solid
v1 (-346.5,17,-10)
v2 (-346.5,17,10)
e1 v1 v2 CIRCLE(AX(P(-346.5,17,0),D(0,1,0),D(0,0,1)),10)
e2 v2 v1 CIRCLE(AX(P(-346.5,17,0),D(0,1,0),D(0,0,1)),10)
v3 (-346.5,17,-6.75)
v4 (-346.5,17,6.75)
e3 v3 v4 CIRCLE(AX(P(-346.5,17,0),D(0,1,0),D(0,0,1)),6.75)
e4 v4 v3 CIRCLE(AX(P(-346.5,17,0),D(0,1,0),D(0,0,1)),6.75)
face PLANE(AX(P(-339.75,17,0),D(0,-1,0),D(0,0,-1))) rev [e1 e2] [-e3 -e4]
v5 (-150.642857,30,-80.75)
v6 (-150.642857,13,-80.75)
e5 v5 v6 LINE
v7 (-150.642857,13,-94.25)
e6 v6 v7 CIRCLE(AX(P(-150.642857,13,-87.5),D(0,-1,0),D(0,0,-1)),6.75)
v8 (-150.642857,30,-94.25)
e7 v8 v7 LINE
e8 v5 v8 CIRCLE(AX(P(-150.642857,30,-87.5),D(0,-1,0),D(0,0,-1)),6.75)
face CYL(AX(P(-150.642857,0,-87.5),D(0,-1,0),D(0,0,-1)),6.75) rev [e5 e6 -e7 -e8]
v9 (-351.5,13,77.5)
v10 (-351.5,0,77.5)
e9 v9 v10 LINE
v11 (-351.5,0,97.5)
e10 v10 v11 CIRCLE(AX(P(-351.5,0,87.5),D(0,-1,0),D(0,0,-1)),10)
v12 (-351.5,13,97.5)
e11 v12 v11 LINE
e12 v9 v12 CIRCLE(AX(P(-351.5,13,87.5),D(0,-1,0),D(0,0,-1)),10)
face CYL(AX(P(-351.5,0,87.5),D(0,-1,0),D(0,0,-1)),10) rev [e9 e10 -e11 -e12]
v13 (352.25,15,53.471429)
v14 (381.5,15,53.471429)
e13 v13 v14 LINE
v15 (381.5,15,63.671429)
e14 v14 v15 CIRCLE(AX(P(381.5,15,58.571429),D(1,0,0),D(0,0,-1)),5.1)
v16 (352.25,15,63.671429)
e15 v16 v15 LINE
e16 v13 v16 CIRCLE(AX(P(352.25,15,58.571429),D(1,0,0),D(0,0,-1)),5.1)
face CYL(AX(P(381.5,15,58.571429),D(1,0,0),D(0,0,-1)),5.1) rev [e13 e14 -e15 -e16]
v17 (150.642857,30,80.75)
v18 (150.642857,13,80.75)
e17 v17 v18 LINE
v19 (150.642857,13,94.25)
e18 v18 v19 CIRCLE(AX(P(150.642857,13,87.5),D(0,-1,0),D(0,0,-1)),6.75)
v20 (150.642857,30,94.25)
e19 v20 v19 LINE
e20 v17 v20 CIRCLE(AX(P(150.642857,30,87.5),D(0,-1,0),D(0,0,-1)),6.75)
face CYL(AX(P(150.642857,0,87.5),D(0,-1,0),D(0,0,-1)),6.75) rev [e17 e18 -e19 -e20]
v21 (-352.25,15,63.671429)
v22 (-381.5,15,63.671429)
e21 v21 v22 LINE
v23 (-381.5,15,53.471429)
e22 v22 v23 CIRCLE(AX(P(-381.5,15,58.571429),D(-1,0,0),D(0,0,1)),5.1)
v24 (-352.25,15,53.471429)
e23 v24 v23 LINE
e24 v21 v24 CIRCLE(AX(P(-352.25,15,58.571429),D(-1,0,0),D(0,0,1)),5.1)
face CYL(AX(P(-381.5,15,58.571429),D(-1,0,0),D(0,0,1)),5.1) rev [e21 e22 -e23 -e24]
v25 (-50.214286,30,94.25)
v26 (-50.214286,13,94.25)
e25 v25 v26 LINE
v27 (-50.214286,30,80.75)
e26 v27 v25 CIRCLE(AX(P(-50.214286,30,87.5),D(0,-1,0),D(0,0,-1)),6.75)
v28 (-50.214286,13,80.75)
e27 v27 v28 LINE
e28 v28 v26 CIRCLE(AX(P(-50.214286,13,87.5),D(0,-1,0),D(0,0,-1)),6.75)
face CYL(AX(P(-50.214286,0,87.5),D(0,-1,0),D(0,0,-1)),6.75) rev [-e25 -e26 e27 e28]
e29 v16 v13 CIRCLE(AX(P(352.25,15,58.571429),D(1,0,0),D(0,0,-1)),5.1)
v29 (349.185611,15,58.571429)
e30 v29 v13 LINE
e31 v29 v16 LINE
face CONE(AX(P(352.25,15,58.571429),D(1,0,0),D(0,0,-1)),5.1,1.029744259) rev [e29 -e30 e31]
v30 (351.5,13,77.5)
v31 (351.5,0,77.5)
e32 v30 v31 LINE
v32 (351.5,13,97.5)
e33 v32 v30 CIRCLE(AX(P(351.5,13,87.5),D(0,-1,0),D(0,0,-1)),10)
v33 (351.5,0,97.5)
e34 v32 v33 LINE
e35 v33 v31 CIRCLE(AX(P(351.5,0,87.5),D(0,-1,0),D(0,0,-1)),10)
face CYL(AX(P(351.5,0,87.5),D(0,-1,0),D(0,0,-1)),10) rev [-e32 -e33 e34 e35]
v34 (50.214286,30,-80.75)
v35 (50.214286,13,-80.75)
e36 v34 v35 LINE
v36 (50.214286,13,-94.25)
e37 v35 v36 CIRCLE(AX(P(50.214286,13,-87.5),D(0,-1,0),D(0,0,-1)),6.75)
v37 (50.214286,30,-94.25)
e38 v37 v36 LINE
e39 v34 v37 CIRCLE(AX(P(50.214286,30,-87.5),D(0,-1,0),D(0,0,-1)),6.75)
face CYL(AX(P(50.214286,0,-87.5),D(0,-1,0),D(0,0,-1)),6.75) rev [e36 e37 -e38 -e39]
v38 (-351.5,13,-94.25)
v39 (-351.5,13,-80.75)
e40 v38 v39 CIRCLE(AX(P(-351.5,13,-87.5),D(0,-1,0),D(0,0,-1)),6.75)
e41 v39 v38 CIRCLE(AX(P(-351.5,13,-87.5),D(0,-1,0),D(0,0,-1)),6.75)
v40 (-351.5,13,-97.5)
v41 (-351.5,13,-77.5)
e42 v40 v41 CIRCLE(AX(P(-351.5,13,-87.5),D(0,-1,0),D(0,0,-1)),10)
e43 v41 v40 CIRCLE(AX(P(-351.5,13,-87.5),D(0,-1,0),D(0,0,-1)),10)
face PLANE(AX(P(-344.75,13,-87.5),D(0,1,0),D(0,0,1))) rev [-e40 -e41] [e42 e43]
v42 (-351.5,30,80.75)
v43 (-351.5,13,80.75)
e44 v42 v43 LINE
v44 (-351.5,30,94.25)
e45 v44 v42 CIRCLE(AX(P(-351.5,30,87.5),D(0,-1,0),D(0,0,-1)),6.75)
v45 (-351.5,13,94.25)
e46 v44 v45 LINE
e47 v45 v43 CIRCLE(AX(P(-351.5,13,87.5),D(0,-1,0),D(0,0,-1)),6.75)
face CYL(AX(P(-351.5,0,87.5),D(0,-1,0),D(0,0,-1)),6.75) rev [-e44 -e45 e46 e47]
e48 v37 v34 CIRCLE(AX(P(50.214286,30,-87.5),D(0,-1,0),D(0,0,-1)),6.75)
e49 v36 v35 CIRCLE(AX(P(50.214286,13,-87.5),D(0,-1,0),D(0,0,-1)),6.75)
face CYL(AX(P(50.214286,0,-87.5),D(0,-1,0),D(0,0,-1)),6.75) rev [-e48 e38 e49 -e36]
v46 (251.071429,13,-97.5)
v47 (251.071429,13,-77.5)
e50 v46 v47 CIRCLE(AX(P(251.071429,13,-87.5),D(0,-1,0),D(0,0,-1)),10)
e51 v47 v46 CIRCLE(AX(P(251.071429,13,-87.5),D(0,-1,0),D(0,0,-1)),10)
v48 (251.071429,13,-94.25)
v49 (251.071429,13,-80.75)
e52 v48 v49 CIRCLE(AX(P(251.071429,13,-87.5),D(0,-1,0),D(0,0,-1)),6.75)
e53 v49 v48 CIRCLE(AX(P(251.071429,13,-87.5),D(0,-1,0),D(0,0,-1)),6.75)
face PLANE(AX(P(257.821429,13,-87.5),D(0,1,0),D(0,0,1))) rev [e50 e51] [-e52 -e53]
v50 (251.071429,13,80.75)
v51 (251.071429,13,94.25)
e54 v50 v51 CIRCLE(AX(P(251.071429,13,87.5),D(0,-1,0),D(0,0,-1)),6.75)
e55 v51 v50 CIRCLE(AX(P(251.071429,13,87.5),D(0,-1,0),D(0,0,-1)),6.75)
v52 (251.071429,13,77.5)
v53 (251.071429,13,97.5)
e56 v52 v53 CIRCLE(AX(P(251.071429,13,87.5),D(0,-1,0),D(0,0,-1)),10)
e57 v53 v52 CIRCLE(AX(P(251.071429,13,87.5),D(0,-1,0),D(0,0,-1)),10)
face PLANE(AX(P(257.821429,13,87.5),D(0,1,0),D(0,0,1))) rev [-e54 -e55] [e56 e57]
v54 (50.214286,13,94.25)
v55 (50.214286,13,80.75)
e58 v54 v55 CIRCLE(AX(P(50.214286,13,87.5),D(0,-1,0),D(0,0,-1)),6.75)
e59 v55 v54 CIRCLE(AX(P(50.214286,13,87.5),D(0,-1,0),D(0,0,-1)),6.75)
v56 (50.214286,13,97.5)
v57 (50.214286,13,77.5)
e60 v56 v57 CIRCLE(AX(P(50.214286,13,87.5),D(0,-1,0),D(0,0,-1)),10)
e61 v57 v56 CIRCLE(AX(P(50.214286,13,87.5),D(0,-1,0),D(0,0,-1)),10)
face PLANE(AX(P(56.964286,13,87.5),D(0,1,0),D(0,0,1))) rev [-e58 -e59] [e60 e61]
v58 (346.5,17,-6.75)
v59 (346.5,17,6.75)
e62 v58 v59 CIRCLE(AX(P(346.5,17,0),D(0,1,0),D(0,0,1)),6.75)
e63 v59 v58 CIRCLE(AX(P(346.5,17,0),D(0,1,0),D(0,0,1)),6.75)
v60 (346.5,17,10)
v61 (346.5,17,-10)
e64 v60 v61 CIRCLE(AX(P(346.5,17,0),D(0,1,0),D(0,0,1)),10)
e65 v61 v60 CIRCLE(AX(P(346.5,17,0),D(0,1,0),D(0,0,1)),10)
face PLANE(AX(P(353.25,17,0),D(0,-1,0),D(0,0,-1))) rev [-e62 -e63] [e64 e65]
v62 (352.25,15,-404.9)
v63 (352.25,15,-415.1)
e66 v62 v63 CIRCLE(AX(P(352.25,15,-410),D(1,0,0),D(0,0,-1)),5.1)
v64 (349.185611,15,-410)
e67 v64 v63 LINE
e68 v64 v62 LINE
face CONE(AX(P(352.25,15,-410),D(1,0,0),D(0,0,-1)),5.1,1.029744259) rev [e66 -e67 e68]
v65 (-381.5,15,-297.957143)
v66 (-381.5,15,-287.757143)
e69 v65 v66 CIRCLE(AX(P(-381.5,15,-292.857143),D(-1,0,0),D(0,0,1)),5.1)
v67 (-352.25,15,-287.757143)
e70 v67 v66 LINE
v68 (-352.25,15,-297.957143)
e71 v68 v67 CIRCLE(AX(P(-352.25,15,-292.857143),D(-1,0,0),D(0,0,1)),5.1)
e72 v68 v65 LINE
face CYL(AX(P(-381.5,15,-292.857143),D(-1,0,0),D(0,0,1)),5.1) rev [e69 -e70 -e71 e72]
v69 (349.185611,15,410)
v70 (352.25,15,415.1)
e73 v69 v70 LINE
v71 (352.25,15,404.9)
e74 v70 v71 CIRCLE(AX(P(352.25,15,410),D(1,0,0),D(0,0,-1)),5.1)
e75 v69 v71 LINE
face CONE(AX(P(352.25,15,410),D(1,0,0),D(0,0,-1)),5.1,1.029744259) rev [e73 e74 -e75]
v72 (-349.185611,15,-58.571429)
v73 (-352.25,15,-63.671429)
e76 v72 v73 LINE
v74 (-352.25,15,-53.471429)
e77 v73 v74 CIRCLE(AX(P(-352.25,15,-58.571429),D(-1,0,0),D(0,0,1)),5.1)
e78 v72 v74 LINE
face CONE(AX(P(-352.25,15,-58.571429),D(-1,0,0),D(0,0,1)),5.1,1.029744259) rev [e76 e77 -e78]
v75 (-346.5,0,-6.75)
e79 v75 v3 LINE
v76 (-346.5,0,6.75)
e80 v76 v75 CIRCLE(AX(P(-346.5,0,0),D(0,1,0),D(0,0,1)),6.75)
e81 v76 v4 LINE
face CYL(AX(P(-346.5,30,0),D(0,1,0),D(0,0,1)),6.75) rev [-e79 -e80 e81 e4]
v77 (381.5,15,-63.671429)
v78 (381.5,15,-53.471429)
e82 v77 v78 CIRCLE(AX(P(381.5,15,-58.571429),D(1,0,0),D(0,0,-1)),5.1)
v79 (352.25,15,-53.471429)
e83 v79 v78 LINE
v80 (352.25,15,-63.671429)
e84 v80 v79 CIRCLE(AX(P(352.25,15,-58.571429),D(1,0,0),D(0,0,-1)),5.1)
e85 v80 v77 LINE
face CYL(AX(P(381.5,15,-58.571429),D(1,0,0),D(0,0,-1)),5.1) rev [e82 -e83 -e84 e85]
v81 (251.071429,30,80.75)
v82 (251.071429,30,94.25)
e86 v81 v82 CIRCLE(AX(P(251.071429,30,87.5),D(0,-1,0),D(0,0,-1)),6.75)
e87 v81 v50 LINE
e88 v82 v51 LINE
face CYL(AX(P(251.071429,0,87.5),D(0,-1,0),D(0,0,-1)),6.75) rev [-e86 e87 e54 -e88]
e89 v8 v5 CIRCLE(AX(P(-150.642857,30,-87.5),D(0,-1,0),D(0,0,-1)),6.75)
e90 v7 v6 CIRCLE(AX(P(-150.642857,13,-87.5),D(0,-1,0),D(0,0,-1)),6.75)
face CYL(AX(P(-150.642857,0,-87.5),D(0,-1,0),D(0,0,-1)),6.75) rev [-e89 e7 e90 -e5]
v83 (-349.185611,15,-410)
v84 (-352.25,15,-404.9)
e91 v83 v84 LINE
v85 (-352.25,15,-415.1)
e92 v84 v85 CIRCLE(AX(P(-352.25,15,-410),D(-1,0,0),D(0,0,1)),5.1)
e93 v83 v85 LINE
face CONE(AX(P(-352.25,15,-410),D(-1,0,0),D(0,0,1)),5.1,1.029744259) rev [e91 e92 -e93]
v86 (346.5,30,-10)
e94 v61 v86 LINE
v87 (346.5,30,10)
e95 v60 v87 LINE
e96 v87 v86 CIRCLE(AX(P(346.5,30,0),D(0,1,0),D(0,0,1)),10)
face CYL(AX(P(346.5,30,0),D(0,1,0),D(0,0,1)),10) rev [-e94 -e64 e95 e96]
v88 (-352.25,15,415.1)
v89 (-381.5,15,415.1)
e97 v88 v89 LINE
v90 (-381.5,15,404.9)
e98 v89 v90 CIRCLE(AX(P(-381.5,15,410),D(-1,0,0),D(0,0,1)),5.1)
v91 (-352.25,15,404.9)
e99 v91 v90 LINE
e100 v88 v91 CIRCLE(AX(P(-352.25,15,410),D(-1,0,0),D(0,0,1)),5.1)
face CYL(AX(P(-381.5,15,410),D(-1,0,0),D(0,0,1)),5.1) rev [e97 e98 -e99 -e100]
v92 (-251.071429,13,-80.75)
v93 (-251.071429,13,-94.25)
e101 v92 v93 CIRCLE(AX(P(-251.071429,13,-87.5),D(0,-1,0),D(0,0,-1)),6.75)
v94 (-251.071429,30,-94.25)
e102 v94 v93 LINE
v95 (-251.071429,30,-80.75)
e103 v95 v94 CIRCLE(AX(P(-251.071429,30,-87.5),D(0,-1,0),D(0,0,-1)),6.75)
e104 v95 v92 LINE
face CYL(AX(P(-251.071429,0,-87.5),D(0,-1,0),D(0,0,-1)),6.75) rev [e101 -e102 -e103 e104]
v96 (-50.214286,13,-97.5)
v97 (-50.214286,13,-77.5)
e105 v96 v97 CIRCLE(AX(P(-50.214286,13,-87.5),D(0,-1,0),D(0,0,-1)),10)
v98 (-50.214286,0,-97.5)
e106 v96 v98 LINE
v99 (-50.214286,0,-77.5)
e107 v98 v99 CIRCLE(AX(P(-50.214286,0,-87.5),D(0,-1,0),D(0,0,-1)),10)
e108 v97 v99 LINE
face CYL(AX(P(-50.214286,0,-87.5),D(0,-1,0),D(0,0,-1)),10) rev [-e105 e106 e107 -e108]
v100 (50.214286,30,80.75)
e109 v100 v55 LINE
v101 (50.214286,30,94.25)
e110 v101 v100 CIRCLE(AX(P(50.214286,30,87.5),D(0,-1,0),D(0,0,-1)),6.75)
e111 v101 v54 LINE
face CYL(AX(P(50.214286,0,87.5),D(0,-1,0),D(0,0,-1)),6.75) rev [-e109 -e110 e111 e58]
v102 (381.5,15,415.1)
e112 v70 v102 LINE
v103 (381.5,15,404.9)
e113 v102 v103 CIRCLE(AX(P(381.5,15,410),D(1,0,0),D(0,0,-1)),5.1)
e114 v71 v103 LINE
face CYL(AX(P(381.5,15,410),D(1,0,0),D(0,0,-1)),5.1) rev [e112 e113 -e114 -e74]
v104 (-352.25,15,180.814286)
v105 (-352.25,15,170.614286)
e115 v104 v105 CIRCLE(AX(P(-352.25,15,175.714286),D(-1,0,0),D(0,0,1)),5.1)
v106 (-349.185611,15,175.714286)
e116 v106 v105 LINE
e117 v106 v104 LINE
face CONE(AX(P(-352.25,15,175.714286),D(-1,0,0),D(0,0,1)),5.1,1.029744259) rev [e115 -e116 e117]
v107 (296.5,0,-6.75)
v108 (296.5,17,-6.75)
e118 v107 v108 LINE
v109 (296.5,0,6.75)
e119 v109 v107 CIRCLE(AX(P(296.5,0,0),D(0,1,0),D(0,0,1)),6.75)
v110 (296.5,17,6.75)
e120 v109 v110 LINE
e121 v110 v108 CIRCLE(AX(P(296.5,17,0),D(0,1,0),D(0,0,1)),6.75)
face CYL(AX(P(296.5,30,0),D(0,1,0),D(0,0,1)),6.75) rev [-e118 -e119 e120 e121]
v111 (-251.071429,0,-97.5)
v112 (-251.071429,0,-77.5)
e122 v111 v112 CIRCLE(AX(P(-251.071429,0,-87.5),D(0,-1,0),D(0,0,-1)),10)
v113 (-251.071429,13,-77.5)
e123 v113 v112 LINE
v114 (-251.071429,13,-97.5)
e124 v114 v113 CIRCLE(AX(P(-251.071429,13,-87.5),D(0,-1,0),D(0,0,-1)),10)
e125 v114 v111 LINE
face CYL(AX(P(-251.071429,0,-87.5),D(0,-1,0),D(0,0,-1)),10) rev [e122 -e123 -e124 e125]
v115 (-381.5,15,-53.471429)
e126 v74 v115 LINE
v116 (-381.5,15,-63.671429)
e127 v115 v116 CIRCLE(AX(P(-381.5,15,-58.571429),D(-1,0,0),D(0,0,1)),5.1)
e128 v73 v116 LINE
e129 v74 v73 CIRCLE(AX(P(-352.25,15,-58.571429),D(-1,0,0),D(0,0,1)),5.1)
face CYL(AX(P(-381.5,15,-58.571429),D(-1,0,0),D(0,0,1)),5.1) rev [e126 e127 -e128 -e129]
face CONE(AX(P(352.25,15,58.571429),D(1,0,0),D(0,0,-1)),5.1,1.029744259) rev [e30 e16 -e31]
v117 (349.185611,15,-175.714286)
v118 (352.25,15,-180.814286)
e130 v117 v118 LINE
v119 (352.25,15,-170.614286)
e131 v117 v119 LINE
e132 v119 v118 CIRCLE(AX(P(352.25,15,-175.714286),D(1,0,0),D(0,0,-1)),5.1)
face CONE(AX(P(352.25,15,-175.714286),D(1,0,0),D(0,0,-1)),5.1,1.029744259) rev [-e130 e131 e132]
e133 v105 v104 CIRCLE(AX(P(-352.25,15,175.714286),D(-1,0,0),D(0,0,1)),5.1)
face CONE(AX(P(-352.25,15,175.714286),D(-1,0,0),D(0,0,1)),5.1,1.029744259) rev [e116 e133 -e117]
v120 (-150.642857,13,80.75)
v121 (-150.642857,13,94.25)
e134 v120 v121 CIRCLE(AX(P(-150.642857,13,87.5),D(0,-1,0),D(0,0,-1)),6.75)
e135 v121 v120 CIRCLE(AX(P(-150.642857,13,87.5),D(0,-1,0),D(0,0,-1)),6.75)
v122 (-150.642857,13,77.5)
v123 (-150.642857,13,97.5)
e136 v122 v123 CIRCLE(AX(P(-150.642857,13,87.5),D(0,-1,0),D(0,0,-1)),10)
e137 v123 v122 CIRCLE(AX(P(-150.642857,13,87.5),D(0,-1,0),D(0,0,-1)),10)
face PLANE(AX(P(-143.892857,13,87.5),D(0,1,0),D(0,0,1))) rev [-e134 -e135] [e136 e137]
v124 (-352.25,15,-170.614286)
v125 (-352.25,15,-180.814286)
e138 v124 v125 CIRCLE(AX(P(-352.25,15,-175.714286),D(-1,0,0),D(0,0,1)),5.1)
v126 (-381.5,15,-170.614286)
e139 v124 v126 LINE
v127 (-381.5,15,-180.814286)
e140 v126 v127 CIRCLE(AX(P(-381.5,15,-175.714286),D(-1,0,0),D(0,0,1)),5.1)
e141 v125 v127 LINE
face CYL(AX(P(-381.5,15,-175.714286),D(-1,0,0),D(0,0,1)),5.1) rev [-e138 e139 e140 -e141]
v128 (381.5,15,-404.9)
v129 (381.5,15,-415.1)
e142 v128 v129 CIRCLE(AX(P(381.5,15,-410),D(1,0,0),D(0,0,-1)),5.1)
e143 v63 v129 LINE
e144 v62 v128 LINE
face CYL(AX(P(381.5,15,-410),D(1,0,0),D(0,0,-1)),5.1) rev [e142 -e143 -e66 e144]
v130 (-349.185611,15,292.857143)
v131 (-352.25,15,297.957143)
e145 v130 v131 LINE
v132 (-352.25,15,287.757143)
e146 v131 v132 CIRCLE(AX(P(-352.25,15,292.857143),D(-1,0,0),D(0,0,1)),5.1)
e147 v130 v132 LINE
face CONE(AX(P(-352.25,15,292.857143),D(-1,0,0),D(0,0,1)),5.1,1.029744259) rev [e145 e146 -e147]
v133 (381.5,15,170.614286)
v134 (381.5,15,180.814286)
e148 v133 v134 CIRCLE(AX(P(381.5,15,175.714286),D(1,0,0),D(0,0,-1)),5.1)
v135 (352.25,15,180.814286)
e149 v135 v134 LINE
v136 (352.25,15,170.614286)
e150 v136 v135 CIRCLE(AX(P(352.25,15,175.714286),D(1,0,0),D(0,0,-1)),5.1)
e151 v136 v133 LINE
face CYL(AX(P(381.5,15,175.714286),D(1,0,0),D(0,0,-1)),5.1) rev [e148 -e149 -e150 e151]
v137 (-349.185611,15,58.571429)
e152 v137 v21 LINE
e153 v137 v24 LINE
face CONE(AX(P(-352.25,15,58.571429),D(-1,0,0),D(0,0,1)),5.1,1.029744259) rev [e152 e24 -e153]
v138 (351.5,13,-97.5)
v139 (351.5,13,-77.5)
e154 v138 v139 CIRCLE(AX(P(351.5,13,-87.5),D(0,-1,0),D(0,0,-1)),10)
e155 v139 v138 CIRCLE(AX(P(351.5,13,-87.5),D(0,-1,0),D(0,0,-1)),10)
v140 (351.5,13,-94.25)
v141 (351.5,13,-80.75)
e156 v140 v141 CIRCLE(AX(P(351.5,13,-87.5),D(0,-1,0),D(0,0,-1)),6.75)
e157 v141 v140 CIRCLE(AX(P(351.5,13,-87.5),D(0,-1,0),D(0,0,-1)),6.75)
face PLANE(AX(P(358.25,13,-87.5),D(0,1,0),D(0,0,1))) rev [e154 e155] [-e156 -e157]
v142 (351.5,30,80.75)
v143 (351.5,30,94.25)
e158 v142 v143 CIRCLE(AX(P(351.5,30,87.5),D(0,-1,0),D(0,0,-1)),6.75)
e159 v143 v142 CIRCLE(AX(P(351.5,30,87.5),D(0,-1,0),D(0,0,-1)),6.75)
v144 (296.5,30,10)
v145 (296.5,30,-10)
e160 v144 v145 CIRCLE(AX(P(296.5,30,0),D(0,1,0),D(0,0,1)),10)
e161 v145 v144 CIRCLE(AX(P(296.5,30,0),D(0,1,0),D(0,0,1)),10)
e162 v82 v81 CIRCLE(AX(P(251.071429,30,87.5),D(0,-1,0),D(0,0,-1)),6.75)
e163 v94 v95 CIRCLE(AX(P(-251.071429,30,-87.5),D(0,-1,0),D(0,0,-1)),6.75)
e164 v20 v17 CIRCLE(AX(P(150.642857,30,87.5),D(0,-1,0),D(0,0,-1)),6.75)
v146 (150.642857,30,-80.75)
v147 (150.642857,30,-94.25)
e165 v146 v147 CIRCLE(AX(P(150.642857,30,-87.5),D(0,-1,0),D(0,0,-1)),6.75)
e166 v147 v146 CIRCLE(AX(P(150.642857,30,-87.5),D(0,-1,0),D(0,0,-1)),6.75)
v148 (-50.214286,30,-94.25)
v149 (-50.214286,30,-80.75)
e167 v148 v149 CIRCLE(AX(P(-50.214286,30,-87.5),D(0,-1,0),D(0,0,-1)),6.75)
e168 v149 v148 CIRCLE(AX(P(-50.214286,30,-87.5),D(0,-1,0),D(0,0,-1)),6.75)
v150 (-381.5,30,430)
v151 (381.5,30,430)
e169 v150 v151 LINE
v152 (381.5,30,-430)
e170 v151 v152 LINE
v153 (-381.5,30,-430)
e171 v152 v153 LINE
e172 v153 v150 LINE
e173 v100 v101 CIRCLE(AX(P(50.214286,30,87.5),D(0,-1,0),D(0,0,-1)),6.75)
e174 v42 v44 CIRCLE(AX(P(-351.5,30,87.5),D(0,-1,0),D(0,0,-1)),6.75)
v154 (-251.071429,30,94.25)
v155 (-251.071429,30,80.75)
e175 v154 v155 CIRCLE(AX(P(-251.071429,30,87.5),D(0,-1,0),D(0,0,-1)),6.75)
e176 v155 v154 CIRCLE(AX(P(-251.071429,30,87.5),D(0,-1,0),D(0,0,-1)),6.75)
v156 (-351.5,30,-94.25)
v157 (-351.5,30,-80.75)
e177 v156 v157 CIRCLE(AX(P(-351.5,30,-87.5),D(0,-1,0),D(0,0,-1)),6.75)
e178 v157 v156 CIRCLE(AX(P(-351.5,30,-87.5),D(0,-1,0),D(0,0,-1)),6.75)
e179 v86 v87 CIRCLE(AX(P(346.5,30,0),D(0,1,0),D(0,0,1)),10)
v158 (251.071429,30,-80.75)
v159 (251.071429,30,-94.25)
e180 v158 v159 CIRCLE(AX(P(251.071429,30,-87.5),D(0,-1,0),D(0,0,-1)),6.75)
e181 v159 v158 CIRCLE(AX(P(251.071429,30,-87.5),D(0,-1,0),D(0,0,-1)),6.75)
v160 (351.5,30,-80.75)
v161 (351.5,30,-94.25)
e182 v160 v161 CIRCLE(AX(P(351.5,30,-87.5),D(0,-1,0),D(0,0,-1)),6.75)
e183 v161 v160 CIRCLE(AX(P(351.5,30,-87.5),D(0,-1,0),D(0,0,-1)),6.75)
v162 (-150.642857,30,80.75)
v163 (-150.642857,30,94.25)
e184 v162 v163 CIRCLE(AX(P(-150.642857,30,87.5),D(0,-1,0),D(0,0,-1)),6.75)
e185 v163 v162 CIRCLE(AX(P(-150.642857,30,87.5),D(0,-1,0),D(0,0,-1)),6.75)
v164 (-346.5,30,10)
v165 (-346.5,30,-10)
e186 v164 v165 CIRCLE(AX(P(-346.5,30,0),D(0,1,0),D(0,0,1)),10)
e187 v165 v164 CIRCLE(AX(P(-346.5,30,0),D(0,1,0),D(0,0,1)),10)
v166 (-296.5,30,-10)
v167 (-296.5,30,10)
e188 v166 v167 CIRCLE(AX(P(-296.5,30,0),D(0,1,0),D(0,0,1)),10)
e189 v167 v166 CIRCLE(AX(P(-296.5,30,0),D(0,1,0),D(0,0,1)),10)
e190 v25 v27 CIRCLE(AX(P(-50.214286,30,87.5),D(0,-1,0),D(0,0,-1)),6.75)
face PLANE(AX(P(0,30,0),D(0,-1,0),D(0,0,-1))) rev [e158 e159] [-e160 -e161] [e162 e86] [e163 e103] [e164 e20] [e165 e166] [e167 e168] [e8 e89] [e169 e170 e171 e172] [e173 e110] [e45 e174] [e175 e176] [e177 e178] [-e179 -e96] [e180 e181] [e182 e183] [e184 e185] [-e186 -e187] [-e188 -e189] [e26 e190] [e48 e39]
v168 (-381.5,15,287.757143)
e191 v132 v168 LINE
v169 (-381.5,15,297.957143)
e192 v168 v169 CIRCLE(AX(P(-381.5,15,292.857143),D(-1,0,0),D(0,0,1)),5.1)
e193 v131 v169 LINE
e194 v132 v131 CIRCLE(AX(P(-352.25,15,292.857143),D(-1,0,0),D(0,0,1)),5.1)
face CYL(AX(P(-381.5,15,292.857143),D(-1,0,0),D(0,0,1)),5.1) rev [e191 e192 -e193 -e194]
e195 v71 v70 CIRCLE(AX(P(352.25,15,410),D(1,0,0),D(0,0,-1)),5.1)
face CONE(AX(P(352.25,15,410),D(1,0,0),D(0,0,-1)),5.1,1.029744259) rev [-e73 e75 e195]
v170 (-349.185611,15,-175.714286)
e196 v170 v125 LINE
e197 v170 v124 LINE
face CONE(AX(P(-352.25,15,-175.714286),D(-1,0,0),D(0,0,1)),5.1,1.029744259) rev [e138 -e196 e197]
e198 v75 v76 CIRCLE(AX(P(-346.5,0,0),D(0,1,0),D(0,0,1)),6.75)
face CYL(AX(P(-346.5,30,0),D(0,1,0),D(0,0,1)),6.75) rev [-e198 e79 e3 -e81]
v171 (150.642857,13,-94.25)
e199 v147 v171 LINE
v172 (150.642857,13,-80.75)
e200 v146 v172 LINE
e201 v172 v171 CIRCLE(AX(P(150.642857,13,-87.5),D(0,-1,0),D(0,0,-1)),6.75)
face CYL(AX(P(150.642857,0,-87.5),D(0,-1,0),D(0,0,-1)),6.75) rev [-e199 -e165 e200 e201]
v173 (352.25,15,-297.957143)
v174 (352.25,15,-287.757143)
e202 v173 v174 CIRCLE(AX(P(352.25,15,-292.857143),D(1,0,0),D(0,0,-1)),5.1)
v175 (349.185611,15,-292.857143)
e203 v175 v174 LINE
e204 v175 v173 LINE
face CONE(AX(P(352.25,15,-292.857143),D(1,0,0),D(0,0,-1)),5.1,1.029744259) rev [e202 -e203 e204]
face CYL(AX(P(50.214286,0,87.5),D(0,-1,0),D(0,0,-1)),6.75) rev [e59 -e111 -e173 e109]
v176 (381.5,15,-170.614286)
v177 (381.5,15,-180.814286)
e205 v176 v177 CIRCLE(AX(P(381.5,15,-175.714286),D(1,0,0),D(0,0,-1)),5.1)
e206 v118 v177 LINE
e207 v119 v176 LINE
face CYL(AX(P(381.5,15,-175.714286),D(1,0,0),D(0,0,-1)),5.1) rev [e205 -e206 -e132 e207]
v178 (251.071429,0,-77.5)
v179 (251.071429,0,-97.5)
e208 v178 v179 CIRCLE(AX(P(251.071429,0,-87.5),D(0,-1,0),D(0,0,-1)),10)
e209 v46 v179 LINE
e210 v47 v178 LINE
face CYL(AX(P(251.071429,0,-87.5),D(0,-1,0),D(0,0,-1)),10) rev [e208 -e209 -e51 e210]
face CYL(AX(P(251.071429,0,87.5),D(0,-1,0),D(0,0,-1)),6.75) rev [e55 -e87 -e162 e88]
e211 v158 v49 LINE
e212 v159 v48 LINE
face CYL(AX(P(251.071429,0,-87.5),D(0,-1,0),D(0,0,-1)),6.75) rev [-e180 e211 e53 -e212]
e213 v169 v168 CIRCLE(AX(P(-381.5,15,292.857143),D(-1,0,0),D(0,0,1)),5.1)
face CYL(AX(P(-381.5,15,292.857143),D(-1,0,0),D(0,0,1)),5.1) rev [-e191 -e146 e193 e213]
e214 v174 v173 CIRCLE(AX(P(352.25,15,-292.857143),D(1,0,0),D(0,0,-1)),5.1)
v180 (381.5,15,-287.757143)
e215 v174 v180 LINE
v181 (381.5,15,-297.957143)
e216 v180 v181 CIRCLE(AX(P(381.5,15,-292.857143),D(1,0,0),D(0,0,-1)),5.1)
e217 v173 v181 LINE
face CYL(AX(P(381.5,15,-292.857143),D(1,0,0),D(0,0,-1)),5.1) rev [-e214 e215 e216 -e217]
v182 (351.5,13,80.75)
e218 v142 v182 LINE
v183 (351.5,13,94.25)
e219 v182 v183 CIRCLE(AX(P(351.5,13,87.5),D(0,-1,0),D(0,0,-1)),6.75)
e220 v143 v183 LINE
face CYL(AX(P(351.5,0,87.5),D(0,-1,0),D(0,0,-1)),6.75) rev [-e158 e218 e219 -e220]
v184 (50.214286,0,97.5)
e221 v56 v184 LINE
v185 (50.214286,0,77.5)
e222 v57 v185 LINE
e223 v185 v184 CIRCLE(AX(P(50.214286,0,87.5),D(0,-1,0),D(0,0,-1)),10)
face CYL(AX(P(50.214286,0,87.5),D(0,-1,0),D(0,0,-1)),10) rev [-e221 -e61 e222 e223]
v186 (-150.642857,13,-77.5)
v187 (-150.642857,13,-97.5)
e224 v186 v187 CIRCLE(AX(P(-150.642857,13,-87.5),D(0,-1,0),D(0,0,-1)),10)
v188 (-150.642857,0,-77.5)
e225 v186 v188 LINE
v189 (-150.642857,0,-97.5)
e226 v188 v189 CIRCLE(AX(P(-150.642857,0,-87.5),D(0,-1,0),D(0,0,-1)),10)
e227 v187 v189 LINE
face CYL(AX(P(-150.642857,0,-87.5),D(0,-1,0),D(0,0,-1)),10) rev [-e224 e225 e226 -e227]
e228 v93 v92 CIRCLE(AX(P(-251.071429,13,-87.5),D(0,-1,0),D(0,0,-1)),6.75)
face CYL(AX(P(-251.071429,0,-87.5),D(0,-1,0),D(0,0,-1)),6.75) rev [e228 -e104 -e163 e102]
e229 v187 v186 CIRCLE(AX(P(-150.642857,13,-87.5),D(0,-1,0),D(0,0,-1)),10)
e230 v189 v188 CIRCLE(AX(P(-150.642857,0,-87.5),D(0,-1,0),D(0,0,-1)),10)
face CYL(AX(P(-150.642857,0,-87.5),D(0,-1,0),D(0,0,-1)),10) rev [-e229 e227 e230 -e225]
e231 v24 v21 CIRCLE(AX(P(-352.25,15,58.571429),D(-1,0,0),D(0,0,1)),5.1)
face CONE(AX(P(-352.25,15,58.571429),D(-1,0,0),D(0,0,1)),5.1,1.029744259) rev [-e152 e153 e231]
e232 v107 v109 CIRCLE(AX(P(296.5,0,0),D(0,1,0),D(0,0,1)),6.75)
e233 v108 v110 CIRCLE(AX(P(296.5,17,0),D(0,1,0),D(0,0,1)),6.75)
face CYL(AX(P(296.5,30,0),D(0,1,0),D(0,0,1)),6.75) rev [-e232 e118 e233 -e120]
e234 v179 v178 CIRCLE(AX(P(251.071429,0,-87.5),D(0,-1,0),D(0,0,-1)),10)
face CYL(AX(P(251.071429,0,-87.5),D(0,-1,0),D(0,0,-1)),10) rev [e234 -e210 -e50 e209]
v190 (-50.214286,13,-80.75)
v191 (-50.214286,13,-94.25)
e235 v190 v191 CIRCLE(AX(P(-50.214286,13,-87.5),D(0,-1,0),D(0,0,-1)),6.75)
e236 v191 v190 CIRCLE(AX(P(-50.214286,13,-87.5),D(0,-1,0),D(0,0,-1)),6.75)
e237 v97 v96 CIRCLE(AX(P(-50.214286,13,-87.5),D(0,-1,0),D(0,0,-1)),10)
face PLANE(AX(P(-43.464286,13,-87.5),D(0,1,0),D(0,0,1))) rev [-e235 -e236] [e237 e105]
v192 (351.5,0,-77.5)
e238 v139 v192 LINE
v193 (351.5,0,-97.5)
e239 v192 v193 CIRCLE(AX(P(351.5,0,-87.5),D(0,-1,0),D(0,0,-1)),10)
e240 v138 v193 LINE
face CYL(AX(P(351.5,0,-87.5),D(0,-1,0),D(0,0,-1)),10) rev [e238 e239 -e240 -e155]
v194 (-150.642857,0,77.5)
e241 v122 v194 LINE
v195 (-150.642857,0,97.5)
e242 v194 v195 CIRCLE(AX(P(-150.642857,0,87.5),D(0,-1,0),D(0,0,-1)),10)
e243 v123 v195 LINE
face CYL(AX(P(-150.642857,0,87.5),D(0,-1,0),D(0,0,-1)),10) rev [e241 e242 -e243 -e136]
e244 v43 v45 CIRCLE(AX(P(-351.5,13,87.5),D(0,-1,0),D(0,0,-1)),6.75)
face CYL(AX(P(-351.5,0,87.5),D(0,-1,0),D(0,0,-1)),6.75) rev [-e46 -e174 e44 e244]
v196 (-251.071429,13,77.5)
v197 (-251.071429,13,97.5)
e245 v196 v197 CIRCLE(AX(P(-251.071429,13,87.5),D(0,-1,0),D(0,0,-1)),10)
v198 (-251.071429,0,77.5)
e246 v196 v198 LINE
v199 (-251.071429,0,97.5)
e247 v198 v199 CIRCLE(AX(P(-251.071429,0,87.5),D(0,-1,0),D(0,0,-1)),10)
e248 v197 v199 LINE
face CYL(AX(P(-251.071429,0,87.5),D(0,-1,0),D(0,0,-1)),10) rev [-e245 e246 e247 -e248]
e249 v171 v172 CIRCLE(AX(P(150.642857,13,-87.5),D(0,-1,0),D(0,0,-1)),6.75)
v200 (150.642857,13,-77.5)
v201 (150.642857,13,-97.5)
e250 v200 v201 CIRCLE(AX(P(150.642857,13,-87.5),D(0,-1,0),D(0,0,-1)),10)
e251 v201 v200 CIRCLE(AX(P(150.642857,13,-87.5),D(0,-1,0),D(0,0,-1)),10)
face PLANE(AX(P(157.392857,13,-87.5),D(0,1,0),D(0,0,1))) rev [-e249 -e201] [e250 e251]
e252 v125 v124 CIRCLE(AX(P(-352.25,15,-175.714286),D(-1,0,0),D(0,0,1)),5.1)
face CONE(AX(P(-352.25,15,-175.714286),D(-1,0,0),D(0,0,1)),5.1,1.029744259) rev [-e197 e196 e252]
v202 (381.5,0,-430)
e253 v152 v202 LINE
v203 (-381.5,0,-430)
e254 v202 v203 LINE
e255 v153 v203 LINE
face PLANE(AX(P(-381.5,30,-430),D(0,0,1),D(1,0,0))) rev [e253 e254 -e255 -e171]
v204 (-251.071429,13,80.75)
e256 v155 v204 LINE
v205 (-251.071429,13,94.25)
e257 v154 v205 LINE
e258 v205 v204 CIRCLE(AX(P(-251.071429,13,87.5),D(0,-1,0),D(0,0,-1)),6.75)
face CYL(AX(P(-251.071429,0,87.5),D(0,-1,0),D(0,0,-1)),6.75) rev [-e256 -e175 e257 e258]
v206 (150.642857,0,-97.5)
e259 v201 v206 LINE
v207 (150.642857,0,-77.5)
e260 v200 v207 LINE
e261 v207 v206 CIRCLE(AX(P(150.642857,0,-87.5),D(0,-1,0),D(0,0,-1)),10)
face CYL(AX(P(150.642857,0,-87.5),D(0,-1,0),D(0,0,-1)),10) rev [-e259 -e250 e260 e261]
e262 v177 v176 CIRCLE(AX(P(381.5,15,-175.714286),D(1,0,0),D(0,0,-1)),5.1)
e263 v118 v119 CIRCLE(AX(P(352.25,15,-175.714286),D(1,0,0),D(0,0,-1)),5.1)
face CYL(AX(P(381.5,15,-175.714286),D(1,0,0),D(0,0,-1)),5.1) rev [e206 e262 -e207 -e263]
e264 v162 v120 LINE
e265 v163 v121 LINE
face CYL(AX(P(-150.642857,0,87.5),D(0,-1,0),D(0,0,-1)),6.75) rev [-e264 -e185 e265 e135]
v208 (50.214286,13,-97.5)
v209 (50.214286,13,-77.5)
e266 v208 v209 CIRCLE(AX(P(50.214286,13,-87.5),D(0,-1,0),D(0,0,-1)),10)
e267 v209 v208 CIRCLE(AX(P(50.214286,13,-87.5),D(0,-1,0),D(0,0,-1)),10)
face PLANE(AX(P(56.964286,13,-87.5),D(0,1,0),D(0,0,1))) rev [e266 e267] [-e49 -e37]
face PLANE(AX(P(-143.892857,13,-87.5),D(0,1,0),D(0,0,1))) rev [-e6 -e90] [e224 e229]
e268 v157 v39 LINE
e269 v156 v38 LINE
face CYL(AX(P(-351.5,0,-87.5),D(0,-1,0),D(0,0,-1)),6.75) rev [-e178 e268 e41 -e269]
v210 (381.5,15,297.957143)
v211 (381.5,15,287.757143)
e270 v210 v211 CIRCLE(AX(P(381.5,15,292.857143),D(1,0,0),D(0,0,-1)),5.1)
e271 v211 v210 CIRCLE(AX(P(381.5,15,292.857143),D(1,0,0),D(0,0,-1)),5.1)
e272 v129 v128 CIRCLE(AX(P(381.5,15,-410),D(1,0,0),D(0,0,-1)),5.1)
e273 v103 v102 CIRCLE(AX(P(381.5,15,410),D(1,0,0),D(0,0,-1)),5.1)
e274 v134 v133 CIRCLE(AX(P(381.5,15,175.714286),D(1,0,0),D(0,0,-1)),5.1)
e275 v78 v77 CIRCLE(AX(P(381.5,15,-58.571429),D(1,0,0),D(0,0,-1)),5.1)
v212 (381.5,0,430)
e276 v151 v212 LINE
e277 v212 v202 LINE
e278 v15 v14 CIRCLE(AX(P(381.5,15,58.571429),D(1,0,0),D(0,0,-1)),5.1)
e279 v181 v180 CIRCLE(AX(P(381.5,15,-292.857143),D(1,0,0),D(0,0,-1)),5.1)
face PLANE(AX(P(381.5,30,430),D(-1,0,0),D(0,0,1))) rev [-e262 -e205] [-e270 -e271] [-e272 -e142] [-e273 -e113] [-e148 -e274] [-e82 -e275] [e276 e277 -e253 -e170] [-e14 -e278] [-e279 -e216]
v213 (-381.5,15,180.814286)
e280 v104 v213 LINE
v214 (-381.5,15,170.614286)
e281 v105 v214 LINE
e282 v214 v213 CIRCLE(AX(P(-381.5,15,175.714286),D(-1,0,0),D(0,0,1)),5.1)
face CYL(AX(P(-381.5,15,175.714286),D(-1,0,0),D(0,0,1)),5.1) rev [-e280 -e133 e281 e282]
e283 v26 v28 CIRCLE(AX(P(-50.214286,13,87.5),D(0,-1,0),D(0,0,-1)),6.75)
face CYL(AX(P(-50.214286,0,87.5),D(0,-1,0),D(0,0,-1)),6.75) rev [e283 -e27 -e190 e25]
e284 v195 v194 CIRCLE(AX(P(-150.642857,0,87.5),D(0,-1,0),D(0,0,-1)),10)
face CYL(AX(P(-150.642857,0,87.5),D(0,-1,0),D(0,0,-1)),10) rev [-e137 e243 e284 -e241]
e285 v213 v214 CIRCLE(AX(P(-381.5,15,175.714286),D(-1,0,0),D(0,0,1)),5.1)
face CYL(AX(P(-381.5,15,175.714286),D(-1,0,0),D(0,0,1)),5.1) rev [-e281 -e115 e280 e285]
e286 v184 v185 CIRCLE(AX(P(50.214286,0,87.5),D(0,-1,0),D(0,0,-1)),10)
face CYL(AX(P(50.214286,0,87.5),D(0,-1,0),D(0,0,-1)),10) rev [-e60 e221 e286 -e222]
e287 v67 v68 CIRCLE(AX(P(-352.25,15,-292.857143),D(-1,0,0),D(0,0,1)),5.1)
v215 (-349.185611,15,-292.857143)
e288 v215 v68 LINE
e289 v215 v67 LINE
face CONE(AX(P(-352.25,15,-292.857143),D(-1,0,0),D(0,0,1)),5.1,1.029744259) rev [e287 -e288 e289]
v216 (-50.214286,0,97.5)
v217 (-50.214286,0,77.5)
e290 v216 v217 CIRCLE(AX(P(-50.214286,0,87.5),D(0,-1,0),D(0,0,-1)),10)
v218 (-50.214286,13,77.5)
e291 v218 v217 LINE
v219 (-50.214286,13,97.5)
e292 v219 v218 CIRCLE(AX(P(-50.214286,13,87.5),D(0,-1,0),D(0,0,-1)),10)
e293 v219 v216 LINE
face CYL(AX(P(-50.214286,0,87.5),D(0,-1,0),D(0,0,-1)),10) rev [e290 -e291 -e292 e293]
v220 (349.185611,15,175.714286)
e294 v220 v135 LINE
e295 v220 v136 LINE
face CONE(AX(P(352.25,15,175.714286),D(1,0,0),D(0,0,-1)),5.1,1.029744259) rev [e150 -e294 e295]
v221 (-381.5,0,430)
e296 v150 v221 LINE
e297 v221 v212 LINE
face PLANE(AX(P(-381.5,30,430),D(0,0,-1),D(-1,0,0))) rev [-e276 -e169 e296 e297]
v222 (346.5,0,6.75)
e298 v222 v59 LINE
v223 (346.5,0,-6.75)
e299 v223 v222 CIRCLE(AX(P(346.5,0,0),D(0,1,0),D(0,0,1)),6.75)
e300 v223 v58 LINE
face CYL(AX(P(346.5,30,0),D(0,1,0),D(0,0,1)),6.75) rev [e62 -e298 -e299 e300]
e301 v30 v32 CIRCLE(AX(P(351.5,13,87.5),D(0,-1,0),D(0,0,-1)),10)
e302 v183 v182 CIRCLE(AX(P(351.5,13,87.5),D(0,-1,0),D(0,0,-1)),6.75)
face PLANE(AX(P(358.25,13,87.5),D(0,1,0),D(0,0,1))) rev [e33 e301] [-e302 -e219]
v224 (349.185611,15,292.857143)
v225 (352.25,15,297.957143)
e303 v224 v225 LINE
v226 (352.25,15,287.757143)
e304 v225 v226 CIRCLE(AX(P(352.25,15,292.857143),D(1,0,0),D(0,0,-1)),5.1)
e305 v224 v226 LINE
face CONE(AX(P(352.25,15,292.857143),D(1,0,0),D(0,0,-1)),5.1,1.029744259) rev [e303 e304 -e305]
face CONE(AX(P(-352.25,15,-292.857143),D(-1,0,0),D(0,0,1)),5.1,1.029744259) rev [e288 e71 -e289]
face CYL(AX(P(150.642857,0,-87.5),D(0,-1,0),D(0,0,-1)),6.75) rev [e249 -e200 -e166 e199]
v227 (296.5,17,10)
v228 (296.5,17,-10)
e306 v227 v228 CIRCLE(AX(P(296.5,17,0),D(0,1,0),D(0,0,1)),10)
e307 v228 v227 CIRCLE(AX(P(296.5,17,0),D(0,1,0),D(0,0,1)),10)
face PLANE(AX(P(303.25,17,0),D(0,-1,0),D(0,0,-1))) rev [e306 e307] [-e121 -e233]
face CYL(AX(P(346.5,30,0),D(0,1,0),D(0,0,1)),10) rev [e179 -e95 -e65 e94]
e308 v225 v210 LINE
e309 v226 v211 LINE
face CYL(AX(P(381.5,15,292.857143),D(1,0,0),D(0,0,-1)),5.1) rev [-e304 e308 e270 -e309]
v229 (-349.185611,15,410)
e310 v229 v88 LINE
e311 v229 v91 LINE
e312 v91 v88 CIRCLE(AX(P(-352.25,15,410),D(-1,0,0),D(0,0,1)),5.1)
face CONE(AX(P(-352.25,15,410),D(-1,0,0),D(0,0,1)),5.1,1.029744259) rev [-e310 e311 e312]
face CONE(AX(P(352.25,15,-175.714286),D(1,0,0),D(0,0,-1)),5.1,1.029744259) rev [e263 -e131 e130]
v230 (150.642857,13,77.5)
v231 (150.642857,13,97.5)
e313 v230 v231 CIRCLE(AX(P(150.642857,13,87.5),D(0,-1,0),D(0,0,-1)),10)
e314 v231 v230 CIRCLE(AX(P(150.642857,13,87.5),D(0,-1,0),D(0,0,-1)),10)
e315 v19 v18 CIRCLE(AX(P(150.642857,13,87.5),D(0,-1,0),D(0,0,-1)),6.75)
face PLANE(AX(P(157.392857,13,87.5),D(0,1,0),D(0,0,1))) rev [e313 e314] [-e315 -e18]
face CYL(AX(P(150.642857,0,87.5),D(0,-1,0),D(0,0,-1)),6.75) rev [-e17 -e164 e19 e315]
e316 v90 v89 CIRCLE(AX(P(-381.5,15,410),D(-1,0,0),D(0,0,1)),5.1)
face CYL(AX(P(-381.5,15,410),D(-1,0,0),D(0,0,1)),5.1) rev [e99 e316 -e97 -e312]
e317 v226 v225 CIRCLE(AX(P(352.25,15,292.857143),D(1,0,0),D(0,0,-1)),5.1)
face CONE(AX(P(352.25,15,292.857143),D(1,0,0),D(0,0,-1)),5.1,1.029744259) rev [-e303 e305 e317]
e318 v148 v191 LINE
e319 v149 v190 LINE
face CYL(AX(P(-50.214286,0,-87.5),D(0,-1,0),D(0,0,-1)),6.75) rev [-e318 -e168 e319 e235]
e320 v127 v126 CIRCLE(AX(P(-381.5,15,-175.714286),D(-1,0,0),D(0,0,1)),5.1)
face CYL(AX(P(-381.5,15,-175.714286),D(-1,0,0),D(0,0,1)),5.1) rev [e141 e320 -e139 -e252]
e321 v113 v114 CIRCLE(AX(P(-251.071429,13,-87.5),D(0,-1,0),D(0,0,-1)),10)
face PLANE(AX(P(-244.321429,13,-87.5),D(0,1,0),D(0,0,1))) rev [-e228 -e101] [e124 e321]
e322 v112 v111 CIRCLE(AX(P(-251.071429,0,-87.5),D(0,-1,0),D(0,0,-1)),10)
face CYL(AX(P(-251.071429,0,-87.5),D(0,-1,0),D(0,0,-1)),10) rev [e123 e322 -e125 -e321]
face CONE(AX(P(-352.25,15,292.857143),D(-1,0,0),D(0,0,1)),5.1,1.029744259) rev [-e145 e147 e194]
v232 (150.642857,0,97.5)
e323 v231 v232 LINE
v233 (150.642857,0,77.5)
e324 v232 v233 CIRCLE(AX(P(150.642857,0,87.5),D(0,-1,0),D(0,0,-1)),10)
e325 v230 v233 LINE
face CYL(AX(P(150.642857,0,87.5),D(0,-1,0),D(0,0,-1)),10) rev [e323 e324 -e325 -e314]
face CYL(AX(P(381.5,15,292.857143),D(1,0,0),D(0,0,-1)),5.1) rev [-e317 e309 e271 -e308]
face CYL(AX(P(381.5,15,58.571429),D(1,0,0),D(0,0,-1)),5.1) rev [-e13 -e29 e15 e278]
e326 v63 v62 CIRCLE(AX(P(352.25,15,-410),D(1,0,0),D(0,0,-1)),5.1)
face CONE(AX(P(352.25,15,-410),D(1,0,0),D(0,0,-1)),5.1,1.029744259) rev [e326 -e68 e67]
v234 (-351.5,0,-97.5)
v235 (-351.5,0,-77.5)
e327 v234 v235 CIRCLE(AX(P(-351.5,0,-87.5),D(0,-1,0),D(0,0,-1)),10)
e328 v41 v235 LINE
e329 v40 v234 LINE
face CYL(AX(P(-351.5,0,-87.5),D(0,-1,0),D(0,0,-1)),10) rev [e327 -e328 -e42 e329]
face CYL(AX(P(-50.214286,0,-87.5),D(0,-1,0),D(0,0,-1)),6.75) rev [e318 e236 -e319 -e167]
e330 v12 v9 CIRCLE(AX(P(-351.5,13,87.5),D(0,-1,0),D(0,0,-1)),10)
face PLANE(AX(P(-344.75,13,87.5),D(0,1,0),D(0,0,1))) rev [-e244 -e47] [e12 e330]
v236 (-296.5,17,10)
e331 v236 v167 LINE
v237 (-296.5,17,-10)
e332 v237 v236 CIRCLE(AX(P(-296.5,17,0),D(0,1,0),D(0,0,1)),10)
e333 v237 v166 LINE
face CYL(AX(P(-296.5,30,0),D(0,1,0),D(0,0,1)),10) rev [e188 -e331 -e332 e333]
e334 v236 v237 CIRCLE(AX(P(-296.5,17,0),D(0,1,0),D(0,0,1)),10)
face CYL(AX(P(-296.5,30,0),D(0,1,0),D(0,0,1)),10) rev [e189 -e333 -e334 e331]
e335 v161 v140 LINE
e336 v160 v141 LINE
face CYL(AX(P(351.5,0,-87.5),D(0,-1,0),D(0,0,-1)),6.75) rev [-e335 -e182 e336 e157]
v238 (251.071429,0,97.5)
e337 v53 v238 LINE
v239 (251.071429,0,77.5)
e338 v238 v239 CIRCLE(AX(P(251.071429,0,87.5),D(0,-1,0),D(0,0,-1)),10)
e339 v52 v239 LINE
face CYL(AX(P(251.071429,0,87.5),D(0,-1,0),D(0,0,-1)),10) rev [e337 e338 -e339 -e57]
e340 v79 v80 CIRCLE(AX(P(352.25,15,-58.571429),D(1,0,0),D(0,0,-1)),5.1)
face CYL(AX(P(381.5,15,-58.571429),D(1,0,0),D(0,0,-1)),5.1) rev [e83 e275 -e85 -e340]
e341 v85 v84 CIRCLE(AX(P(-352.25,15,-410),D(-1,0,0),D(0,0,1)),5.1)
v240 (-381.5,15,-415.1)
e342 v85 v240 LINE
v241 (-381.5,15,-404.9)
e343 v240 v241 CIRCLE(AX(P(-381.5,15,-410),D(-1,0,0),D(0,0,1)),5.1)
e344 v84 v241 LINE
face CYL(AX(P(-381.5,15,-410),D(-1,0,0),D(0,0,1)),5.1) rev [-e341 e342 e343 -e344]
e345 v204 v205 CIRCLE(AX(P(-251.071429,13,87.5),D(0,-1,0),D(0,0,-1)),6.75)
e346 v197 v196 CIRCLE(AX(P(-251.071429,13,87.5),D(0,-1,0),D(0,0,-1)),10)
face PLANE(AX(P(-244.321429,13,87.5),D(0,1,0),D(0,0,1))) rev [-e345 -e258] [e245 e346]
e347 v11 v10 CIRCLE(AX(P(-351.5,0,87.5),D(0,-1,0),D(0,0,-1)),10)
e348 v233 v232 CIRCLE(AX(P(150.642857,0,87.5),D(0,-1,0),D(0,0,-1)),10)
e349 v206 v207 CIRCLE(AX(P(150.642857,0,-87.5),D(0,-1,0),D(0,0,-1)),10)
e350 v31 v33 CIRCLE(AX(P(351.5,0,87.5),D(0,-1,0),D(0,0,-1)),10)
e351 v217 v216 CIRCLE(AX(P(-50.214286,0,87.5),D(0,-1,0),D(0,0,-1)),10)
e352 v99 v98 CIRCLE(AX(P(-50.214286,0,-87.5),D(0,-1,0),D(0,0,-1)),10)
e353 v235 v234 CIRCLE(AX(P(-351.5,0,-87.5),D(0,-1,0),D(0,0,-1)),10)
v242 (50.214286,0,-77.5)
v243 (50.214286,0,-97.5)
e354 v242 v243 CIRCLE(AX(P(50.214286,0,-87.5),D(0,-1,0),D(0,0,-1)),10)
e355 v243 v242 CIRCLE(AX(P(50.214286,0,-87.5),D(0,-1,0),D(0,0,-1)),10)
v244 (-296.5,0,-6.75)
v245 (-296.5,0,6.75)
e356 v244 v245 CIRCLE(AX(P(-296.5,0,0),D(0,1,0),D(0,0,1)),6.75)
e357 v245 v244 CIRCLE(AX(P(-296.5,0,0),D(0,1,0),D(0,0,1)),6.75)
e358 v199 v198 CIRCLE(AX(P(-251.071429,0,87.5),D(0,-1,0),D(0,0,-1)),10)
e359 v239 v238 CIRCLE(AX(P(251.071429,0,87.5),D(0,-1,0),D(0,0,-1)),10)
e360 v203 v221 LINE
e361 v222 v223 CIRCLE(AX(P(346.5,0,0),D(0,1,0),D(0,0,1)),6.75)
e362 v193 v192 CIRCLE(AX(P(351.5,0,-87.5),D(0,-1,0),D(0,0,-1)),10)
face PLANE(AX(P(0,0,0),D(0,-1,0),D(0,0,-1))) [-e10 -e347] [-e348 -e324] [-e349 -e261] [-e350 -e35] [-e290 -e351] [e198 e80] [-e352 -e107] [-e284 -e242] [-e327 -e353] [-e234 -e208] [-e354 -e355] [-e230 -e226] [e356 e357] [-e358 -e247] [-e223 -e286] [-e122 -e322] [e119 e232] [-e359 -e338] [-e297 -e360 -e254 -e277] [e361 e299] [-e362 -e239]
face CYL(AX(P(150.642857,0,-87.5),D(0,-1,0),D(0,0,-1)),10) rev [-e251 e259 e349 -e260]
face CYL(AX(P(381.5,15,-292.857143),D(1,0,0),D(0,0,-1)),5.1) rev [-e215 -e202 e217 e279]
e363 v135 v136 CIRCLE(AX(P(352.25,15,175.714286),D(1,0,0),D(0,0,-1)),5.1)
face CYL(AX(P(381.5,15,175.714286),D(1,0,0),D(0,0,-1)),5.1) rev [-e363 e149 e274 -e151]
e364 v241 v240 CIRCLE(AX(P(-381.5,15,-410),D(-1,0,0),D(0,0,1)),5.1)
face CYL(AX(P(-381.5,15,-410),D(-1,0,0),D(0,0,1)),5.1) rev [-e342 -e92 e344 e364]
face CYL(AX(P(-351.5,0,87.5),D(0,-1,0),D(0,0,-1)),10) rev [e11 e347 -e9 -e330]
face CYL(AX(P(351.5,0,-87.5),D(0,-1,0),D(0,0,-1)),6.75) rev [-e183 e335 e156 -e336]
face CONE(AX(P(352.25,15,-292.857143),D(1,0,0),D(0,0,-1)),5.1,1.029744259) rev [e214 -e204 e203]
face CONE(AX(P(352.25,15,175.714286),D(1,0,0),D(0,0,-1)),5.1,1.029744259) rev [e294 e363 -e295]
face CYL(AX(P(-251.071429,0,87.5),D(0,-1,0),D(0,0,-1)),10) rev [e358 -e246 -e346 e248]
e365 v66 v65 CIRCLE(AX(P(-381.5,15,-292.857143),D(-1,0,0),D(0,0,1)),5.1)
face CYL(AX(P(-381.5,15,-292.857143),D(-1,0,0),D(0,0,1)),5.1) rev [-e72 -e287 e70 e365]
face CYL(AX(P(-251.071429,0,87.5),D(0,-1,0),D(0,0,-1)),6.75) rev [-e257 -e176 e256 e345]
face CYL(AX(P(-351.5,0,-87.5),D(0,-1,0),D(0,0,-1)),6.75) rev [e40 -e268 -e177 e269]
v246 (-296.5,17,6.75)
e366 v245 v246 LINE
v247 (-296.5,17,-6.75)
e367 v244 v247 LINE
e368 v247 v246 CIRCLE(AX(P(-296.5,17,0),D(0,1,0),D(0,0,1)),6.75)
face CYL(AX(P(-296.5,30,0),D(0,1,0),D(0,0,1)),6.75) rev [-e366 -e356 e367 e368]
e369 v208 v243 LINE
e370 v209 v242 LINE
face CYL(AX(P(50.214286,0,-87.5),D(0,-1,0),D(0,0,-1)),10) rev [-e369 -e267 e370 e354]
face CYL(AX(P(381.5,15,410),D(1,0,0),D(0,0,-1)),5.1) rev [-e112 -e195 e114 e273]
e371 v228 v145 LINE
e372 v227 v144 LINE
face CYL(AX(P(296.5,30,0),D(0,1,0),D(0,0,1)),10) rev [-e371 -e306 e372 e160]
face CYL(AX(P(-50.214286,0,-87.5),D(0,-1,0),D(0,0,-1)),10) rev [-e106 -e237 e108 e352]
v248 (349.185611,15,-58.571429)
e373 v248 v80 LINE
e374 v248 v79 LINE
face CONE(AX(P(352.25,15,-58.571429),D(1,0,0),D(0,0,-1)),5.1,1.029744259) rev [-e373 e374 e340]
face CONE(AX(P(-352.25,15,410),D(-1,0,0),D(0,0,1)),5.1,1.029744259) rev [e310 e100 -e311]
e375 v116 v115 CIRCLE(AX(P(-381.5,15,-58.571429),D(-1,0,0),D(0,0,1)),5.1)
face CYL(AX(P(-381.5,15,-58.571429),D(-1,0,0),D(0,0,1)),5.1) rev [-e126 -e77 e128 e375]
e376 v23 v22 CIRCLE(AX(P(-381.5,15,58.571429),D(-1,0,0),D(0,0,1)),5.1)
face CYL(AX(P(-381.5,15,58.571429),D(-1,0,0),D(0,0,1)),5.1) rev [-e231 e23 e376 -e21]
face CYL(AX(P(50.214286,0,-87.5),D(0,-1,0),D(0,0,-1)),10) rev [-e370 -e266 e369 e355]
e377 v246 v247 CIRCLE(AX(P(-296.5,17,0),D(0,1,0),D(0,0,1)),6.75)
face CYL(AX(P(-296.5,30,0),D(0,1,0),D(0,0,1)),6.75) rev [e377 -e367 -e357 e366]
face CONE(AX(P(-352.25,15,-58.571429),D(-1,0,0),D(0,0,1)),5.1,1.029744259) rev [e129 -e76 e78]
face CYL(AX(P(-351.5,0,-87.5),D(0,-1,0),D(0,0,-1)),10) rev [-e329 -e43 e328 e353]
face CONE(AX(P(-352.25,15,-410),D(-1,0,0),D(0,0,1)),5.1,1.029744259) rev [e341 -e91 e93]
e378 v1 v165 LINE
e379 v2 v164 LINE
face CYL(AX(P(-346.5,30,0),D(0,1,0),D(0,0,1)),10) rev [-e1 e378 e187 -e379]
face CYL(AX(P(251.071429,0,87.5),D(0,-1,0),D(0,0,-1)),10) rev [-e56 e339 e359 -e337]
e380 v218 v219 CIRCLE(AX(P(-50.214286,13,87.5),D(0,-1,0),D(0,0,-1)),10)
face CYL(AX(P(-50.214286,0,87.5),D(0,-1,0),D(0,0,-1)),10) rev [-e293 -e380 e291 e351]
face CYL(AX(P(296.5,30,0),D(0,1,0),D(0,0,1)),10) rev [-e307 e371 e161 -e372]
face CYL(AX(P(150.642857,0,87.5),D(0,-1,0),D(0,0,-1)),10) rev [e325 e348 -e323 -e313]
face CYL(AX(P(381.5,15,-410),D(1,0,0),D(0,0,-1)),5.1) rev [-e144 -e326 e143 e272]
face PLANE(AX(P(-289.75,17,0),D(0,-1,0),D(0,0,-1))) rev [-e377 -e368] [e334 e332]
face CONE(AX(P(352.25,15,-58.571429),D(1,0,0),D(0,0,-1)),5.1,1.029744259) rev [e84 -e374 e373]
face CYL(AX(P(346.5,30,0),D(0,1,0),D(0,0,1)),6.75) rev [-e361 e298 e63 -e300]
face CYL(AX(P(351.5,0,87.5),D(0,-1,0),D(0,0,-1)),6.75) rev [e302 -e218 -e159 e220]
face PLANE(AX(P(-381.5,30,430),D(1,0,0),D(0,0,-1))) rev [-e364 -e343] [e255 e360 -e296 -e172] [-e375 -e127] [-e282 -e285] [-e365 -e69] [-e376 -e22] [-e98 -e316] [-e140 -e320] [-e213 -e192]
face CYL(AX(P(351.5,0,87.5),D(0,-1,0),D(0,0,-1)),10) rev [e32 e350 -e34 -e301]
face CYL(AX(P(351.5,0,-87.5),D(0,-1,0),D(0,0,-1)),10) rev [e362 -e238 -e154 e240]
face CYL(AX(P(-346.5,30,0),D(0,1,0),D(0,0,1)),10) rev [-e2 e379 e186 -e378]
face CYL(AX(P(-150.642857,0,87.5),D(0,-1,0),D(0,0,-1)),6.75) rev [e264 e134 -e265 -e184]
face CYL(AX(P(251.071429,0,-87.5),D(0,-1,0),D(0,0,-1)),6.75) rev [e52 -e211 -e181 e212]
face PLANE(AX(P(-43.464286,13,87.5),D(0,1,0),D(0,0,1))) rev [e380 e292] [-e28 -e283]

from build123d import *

# Parameters (mm, degrees)
SKETCH_1_W                = 763
SKETCH_1_H                = 860
EXTRUDE_1_DEPTH           = 30
HOLE_WIZARD_1_D           = 13.5
HOLE_WIZARD_1_CBORE_D     = 20
HOLE_WIZARD_1_CBORE_DEPTH = 13
HOLE_WIZARD_2_D           = 13.5
HOLE_WIZARD_2_CBORE_D     = 20
HOLE_WIZARD_2_CBORE_DEPTH = 13
HOLE_WIZARD_M12_1_D       = 10.2
HOLE_WIZARD_M12_1_DEPTH   = 29.25
HOLE_WIZARD_M12_1_TIP     = 3.064389157
HOLE_WIZARD_M12_2_D       = 10.2
HOLE_WIZARD_M12_2_DEPTH   = 29.25
HOLE_WIZARD_M12_2_TIP     = 3.064389157


with BuildPart() as part:
    # 草图1 → 凸台-拉伸1 (new body)
    with BuildSketch(Plane(origin=(0, 0, 0), x_dir=(1, 0, 0), z_dir=(0, 1, 0))):
        Rectangle(SKETCH_1_W, SKETCH_1_H)
    extrude(amount=EXTRUDE_1_DEPTH)

    # 打孔尺寸(%根据)内六角圆柱头螺钉的类型1 (through all)
    with Locations(Plane(origin=(0, 0, 0), x_dir=(-1, 0, 0), z_dir=(0, -1, 0))):
        with Locations((351.5, 87.5), (351.5, -87.5), (251.071428571, 87.5), (251.071428571, -87.5), (150.642857143, 87.5), (150.642857143, -87.5), (50.214285714, 87.5), (50.214285714, -87.5), (-50.214285714, -87.5), (-50.214285714, 87.5), (-150.642857143, 87.5), (-150.642857143, -87.5), (-251.071428571, 87.5), (-251.071428571, -87.5), (-351.5, -87.5), (-351.5, 87.5)):
            CounterBoreHole(HOLE_WIZARD_1_D / 2, HOLE_WIZARD_1_CBORE_D / 2, HOLE_WIZARD_1_CBORE_DEPTH)

    # 打孔尺寸(%根据)内六角圆柱头螺钉的类型2 (through all)
    with Locations(Plane(origin=(0, 30, 0), x_dir=(1, 0, 0), z_dir=(0, 1, 0))):
        with Locations((-346.5, 0), (-296.5, 0), (346.5, 0), (296.5, 0)):
            CounterBoreHole(HOLE_WIZARD_2_D / 2, HOLE_WIZARD_2_CBORE_D / 2, HOLE_WIZARD_2_CBORE_DEPTH)

    # M12 螺纹孔1
    with Locations(Plane.ZY.offset(381.5)):
        with Locations((410, 15), (292.857142857, 15), (175.714285714, 15), (58.571428571, 15), (-58.571428571, 15), (-175.714285714, 15), (-292.857142857, 15), (-410, 15)):
            Hole(HOLE_WIZARD_M12_1_D / 2, depth=HOLE_WIZARD_M12_1_DEPTH)
            with Locations((0, 0, -(HOLE_WIZARD_M12_1_DEPTH + HOLE_WIZARD_M12_1_TIP / 2))):  # 118° drill point
                Cone(0, HOLE_WIZARD_M12_1_D / 2, HOLE_WIZARD_M12_1_TIP, mode=Mode.SUBTRACT)

    # M12 螺纹孔2
    with Locations(Plane(origin=(381.5, 0, 0), x_dir=(0, 0, -1), z_dir=(1, 0, 0))):
        with Locations((-410, 15), (-292.857142857, 15), (-175.714285714, 15), (-58.571428571, 15), (58.571428571, 15), (175.714285714, 15), (292.857142857, 15), (410, 15)):
            Hole(HOLE_WIZARD_M12_2_D / 2, depth=HOLE_WIZARD_M12_2_DEPTH)
            with Locations((0, 0, -(HOLE_WIZARD_M12_2_DEPTH + HOLE_WIZARD_M12_2_TIP / 2))):  # 118° drill point
                Cone(0, HOLE_WIZARD_M12_2_D / 2, HOLE_WIZARD_M12_2_TIP, mode=Mode.SUBTRACT)


solid = part.part
